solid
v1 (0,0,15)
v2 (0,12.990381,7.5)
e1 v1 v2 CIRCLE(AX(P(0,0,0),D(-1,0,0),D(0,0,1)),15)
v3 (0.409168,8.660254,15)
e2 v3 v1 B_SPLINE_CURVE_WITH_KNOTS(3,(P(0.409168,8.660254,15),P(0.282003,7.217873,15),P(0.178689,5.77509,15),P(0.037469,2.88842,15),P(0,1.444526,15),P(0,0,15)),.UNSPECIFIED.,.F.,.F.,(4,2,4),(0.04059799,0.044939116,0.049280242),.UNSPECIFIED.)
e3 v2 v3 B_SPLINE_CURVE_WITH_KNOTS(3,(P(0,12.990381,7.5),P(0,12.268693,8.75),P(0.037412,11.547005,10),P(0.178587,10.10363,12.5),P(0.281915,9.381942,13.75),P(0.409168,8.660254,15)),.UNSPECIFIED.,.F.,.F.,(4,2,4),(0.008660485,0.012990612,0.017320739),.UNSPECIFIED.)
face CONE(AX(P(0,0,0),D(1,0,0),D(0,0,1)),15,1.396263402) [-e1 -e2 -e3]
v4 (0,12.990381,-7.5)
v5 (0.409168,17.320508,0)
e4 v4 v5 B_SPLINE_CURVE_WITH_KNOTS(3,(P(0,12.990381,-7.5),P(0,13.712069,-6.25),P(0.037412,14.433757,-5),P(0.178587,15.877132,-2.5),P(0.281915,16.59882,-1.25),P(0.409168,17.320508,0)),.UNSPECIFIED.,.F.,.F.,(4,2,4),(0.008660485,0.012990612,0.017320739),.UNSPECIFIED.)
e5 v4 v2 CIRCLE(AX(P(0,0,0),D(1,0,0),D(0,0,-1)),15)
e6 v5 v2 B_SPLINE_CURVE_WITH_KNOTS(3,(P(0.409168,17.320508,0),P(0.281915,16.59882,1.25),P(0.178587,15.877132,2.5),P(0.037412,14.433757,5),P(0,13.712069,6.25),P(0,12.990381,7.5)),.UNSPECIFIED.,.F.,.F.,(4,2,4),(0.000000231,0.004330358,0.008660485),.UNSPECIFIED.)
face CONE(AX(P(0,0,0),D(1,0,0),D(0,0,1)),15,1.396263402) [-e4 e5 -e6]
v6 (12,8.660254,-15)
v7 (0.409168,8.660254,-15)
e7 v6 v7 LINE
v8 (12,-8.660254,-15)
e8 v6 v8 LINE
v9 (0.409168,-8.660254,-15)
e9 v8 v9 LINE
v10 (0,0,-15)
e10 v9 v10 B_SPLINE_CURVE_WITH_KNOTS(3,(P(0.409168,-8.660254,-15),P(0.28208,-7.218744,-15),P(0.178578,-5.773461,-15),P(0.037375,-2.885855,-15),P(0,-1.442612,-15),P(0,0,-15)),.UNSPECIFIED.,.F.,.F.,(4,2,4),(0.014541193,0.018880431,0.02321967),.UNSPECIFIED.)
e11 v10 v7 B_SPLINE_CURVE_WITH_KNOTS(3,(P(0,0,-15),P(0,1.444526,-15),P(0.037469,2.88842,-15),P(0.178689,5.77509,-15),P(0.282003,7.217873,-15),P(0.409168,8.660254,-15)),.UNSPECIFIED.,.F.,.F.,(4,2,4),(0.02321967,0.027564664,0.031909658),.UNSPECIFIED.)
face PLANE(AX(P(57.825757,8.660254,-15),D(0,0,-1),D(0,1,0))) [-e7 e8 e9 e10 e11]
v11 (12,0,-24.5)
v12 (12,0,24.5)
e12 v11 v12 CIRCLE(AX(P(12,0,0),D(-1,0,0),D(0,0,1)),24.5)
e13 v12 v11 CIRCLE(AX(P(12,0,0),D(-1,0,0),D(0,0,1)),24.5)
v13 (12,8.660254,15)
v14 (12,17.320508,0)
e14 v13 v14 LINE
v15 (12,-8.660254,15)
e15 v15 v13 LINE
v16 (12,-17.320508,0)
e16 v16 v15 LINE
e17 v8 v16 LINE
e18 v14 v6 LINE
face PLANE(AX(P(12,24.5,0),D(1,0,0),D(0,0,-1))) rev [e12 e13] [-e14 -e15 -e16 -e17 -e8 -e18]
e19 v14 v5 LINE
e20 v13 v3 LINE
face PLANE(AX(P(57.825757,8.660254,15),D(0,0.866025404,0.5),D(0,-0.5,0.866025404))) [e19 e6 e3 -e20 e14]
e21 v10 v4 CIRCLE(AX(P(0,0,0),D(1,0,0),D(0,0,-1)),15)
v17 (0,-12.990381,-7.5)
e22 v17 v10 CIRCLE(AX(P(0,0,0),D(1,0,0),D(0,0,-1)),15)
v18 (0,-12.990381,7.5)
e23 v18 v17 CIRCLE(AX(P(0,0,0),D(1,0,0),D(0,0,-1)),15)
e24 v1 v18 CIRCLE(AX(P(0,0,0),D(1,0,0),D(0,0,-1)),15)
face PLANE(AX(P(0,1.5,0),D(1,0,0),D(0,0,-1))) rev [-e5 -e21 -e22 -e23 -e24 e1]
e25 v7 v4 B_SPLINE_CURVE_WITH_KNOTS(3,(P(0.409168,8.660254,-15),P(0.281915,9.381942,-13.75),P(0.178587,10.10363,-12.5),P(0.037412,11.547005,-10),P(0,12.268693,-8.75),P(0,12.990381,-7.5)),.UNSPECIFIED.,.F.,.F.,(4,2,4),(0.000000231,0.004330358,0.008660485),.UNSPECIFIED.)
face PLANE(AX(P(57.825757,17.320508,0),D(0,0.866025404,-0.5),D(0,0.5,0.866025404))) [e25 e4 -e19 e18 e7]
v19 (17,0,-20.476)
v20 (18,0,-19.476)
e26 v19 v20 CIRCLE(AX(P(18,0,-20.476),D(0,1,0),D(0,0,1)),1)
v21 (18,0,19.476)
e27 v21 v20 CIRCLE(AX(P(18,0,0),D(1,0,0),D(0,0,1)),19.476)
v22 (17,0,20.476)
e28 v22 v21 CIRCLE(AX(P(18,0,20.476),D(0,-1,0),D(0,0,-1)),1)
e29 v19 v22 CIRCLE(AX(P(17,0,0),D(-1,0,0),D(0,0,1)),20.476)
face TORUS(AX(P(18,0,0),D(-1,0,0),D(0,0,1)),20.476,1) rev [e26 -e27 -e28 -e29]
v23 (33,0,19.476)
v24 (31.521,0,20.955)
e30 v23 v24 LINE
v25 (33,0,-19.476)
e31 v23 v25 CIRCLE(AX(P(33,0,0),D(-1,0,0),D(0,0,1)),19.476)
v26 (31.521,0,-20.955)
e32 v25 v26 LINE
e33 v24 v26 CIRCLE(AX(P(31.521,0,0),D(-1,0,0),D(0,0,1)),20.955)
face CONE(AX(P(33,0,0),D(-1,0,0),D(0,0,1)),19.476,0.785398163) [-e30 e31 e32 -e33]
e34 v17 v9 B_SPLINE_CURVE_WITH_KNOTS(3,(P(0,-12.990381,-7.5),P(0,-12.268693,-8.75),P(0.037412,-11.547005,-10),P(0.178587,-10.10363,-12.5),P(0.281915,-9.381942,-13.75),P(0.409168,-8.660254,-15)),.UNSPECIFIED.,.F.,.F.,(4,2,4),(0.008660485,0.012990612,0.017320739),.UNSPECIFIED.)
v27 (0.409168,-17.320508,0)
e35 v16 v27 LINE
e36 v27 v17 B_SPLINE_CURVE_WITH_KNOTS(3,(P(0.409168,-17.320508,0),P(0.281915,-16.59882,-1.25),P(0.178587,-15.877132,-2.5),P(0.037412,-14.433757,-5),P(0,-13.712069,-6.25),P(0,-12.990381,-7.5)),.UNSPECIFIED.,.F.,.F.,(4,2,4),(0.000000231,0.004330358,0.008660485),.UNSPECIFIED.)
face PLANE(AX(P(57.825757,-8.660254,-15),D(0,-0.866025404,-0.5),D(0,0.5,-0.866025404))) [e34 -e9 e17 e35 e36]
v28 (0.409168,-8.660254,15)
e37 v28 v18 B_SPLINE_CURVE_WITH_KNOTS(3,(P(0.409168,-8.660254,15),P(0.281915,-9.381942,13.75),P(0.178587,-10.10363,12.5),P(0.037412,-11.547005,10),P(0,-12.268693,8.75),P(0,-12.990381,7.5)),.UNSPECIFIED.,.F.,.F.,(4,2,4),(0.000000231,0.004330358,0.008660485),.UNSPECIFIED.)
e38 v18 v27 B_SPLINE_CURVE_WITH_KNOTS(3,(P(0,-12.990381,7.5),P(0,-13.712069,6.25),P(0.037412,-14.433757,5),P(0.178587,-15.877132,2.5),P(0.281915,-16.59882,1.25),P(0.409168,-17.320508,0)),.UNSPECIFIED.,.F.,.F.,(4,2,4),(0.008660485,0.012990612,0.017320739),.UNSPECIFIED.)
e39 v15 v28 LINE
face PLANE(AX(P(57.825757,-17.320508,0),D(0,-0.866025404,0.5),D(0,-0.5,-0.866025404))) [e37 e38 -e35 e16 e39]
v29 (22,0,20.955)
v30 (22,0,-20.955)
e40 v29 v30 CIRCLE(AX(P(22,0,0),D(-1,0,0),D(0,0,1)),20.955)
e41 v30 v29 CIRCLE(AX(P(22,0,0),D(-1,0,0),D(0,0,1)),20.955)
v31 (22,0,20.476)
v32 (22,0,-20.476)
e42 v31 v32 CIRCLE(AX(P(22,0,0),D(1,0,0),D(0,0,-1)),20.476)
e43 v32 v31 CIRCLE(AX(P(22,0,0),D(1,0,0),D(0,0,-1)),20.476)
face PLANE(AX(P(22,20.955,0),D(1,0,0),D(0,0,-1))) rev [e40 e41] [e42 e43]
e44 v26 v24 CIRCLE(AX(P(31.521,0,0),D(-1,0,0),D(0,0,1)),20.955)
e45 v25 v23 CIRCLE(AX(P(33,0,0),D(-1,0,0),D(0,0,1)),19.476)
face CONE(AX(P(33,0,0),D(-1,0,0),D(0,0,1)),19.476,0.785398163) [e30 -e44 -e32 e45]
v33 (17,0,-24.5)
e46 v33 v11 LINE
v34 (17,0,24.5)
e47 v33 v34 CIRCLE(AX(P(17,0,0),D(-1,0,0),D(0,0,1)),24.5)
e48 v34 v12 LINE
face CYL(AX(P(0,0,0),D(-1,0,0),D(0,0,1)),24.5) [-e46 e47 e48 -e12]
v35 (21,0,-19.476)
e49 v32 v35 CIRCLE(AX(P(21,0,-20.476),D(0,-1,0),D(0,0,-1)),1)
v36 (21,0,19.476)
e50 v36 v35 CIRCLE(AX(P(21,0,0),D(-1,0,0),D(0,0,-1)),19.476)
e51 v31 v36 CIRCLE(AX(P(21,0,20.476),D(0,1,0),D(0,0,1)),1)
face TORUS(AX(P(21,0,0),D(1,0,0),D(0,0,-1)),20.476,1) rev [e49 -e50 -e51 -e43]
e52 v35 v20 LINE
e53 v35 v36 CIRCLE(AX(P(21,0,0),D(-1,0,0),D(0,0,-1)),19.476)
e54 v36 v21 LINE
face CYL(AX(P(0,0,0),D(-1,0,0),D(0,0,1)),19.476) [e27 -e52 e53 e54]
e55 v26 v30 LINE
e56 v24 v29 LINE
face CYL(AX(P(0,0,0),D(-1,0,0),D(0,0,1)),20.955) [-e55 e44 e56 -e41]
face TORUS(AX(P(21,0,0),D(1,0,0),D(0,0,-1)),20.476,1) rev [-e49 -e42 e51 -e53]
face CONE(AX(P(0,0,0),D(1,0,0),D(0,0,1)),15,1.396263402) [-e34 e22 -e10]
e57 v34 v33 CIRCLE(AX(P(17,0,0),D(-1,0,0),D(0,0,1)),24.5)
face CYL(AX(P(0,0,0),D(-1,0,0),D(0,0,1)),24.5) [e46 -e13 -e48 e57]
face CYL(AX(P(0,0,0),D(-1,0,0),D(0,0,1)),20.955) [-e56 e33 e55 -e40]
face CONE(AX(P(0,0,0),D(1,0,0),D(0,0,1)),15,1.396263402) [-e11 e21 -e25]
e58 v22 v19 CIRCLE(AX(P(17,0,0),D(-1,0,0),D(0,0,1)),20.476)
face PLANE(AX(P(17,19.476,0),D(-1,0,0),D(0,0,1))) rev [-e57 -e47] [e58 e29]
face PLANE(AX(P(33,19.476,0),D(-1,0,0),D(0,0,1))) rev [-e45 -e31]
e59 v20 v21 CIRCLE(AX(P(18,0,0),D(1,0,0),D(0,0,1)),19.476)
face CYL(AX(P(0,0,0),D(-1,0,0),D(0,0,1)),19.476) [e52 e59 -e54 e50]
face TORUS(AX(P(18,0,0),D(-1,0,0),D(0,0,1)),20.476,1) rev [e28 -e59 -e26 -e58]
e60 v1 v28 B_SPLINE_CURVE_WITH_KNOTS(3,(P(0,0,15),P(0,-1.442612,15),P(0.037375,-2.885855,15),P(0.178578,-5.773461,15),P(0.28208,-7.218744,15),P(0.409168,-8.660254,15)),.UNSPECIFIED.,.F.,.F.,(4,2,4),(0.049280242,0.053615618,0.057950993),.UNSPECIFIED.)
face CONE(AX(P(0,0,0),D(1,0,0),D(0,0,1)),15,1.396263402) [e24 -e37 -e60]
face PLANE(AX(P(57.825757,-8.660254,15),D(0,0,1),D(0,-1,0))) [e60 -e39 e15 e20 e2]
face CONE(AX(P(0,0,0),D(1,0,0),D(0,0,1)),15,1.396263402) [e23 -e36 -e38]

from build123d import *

# Parameters (mm, degrees)
EXTRUDE1_DEPTH     = 12
SKETCH3_OUTSIDE_W  = 179.776
SKETCH3_OUTSIDE_H  = 179.776
SKETCH3_OUTSIDE_R  = 15
CUT_EXTRUDE1_DEPTH = 10
CUT_EXTRUDE1_DRAFT = -80
FILLET1_R          = 1


with BuildPart() as part:
    # Sketch1 → Revolve1 (revolve)
    with BuildSketch(Plane.XY, mode=Mode.PRIVATE) as revolve1_sk:
        Polygon((22, 20.955), (22, 19.476), (17, 19.476), (17, 24.5), (12, 24.5), (12, 1.5), (0, 1.5), (0, 0), (33, 0), (33, 19.476), (31.521, 20.955), align=None)
    revolve(revolve1_sk.sketch.rotate(Axis((0, 0, 0), (1, 0, 0)), 90), axis=Axis((0, 0, 0), (1, 0, 0)))

    # Sketch2 → Extrude1 (add)
    with BuildSketch(Plane.ZY):
        Polygon((0, 17.320508076), (-15, 8.660254038), (-15, -8.660254038), (0, -17.320508076), (15, -8.660254038), (15, 8.660254038), align=None)
    extrude(amount=-EXTRUDE1_DEPTH)


with BuildPart() as cut_extrude1_tool:
    # Sketch3 outside → Cut-Extrude1 (with draft: the straight prism first)
    with BuildSketch(Plane.ZY):
        Rectangle(SKETCH3_OUTSIDE_W, SKETCH3_OUTSIDE_H)
        Circle(SKETCH3_OUTSIDE_R, mode=Mode.SUBTRACT)
    extrude(amount=-CUT_EXTRUDE1_DEPTH)
    # Cut-Extrude1: the draft: its side faces are tilted about the plane it starts from
    cut_extrude1_sides = [cut_extrude1_tool.faces().sort_by_distance(p)[0] for p in [
        (5, -89.888, 0),
        (5, 0, 89.888),
        (5, 89.888, 0),
        (5, 0, -89.888),
        (5, 0, -15),
    ]]
    draft(cut_extrude1_sides, Plane.ZY, CUT_EXTRUDE1_DRAFT)


with BuildPart() as part_1:
    add(part.part)

    # Cut-Extrude1: cut by cut_extrude1_tool
    add(cut_extrude1_tool.part, mode=Mode.SUBTRACT)

    # Fillet1
    fillet1_edges = [part_1.edges().sort_by_distance(p)[0] for p in [
        (22, 0, -19.476),
        (17, 0, -19.476),
    ]]
    fillet(fillet1_edges, radius=FILLET1_R)


solid = part_1.part
